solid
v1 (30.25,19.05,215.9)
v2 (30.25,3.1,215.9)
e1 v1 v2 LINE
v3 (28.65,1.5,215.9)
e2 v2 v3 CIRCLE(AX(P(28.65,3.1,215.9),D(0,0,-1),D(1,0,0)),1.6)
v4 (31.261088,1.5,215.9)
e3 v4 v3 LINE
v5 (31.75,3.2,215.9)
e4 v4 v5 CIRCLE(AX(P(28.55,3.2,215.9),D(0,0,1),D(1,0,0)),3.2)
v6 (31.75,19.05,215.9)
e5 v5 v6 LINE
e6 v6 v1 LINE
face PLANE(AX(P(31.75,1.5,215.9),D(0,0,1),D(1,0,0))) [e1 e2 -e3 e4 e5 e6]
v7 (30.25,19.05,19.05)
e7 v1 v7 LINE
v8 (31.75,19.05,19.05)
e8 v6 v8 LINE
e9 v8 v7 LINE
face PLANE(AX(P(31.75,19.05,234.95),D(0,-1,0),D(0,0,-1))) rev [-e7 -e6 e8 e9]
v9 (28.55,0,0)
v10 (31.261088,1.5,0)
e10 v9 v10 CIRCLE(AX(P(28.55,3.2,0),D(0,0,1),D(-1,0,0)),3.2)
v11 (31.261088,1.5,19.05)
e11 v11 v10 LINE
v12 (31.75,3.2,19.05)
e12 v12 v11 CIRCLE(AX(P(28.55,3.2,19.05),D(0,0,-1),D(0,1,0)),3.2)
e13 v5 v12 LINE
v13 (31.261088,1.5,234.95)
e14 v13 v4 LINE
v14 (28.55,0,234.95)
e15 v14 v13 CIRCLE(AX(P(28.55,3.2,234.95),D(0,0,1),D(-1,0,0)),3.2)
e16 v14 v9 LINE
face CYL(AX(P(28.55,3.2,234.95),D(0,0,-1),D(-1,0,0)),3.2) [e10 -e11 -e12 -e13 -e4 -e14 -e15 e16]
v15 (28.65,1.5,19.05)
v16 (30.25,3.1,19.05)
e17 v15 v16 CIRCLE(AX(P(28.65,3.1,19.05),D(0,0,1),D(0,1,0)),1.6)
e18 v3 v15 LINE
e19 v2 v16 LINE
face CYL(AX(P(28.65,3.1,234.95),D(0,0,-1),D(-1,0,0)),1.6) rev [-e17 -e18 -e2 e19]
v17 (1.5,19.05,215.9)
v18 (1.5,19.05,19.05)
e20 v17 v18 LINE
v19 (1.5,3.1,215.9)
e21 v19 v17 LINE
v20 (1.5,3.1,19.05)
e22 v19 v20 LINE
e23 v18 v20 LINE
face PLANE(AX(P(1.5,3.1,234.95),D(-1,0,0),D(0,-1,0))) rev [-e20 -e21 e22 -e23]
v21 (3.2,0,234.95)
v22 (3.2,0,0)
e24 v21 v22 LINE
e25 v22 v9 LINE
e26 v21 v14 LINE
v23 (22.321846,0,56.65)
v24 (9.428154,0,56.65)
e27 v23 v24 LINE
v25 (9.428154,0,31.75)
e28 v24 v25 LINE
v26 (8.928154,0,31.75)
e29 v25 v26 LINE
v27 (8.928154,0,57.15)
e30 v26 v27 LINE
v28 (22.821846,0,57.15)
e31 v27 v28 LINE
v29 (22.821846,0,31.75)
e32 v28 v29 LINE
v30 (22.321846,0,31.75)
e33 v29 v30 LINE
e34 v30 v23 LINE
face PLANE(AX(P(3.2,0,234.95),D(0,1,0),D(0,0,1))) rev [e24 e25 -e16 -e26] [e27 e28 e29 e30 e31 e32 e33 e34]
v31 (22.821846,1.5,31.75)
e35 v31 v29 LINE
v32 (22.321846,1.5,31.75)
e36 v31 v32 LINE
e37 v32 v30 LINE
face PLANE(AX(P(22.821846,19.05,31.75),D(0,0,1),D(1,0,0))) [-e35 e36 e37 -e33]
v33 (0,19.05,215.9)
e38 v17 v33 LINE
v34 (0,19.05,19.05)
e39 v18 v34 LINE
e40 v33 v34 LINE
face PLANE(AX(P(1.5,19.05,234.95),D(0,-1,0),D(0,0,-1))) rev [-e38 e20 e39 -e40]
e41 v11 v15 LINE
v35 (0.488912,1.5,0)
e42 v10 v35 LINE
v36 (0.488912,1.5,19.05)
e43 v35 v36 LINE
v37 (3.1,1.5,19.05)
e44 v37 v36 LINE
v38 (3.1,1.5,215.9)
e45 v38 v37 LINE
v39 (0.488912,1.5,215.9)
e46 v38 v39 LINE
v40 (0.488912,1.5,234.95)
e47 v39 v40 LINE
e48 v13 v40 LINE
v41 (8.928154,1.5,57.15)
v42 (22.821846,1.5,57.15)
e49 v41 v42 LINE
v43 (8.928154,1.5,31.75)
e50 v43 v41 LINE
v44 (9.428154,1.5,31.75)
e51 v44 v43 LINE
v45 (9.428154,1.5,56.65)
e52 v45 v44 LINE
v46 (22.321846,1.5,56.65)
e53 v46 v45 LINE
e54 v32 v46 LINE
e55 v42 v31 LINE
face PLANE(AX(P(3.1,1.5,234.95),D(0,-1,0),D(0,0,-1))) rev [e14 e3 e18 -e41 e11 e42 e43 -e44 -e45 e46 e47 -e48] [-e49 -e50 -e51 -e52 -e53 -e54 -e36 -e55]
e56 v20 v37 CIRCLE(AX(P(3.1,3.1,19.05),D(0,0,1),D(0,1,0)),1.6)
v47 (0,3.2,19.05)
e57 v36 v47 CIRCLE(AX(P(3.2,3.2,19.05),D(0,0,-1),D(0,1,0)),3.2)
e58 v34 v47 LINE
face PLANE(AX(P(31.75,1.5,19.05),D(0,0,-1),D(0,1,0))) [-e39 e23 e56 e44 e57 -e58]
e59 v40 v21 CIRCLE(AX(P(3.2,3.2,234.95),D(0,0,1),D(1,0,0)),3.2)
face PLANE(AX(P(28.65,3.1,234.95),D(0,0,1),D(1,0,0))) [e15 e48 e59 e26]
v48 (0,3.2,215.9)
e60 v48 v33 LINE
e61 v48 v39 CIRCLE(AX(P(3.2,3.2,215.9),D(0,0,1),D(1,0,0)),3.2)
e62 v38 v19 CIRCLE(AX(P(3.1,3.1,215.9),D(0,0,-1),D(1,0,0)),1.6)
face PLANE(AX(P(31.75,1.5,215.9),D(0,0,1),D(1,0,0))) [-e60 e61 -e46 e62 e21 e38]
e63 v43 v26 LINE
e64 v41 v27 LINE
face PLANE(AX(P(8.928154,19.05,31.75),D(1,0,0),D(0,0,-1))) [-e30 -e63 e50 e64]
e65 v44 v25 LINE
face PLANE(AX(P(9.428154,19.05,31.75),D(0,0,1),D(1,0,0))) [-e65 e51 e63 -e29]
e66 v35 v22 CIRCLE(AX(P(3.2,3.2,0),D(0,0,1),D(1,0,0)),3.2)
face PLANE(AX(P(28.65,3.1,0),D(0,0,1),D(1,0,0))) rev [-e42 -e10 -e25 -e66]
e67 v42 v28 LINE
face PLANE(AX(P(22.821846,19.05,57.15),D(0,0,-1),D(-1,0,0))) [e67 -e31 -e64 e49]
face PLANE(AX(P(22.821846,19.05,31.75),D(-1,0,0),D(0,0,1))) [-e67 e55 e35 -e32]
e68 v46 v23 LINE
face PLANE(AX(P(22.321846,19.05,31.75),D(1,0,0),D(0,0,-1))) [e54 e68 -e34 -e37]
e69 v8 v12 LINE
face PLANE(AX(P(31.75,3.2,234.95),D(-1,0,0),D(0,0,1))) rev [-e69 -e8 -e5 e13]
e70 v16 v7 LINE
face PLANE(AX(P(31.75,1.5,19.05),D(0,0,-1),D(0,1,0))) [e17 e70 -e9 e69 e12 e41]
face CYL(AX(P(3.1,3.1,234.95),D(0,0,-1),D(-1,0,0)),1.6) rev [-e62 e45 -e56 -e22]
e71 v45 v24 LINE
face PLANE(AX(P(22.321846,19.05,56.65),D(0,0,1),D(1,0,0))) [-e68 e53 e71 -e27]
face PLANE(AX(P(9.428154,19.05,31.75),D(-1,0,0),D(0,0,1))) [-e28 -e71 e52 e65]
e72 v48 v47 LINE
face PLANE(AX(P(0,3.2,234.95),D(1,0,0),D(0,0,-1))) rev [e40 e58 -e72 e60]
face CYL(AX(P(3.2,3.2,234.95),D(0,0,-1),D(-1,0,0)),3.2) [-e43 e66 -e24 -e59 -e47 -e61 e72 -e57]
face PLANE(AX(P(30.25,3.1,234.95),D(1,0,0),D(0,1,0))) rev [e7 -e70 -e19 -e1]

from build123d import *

# Parameters (mm, degrees)
BOSS_EXTRUDE1_DEPTH = 234.95
SKETCH2_W           = 19.05
SKETCH2_H           = 17.55
CUT_EXTRUDE1_DEPTH  = 238.849674164
CUT_EXTRUDE2_DEPTH  = 238.849674164


with BuildPart() as part:
    # Sketch1 → Boss-Extrude1 (new body)
    with BuildSketch(Plane.XY):
        with BuildLine():
            Line((30.25, 3.1), (30.25, 19.05))
            Line((30.25, 19.05), (31.75, 19.05))
            Line((31.75, 19.05), (31.75, 3.2))
            ThreePointArc((31.75, 3.2), (30.8127417, 0.9372583), (28.55, 0))
            Line((28.55, 0), (3.2, 0))
            ThreePointArc((3.2, 0), (0.9372583, 0.9372583), (0, 3.2))
            Line((0, 3.2), (0, 19.05))
            Line((0, 19.05), (1.5, 19.05))
            Line((1.5, 19.05), (1.5, 3.1))
            ThreePointArc((1.5, 3.1), (1.96862915, 1.96862915), (3.1, 1.5))
            Line((3.1, 1.5), (28.65, 1.5))
            ThreePointArc((28.65, 1.5), (29.78137085, 1.96862915), (30.25, 3.1))
        make_face()
    extrude(amount=BOSS_EXTRUDE1_DEPTH)

    # Sketch2 → Cut-Extrude1 (cut, through all)
    with BuildSketch(Plane(origin=(0, 0, 0), x_dir=(0, 0, -1), z_dir=(1, 0, 0))):
        with Locations((-9.525, 10.275)):
            Rectangle(SKETCH2_W, SKETCH2_H)
        with Locations((-225.425, 10.275)):
            Rectangle(SKETCH2_W, SKETCH2_H)
    extrude(amount=CUT_EXTRUDE1_DEPTH, mode=Mode.SUBTRACT)

    # Sketch3 → Cut-Extrude2 (cut, through all)
    with BuildSketch(Plane(origin=(0, 0, 0), x_dir=(1, 0, 0), z_dir=(0, 1, 0))):
        Polygon((22.821846385, -57.15), (8.928153615, -57.15), (8.928153615, -31.75), (9.428153615, -31.75), (9.428153615, -56.65), (22.321846385, -56.65), (22.321846385, -31.75), (22.821846385, -31.75), align=None)
    extrude(amount=CUT_EXTRUDE2_DEPTH, mode=Mode.SUBTRACT)


solid = part.part
